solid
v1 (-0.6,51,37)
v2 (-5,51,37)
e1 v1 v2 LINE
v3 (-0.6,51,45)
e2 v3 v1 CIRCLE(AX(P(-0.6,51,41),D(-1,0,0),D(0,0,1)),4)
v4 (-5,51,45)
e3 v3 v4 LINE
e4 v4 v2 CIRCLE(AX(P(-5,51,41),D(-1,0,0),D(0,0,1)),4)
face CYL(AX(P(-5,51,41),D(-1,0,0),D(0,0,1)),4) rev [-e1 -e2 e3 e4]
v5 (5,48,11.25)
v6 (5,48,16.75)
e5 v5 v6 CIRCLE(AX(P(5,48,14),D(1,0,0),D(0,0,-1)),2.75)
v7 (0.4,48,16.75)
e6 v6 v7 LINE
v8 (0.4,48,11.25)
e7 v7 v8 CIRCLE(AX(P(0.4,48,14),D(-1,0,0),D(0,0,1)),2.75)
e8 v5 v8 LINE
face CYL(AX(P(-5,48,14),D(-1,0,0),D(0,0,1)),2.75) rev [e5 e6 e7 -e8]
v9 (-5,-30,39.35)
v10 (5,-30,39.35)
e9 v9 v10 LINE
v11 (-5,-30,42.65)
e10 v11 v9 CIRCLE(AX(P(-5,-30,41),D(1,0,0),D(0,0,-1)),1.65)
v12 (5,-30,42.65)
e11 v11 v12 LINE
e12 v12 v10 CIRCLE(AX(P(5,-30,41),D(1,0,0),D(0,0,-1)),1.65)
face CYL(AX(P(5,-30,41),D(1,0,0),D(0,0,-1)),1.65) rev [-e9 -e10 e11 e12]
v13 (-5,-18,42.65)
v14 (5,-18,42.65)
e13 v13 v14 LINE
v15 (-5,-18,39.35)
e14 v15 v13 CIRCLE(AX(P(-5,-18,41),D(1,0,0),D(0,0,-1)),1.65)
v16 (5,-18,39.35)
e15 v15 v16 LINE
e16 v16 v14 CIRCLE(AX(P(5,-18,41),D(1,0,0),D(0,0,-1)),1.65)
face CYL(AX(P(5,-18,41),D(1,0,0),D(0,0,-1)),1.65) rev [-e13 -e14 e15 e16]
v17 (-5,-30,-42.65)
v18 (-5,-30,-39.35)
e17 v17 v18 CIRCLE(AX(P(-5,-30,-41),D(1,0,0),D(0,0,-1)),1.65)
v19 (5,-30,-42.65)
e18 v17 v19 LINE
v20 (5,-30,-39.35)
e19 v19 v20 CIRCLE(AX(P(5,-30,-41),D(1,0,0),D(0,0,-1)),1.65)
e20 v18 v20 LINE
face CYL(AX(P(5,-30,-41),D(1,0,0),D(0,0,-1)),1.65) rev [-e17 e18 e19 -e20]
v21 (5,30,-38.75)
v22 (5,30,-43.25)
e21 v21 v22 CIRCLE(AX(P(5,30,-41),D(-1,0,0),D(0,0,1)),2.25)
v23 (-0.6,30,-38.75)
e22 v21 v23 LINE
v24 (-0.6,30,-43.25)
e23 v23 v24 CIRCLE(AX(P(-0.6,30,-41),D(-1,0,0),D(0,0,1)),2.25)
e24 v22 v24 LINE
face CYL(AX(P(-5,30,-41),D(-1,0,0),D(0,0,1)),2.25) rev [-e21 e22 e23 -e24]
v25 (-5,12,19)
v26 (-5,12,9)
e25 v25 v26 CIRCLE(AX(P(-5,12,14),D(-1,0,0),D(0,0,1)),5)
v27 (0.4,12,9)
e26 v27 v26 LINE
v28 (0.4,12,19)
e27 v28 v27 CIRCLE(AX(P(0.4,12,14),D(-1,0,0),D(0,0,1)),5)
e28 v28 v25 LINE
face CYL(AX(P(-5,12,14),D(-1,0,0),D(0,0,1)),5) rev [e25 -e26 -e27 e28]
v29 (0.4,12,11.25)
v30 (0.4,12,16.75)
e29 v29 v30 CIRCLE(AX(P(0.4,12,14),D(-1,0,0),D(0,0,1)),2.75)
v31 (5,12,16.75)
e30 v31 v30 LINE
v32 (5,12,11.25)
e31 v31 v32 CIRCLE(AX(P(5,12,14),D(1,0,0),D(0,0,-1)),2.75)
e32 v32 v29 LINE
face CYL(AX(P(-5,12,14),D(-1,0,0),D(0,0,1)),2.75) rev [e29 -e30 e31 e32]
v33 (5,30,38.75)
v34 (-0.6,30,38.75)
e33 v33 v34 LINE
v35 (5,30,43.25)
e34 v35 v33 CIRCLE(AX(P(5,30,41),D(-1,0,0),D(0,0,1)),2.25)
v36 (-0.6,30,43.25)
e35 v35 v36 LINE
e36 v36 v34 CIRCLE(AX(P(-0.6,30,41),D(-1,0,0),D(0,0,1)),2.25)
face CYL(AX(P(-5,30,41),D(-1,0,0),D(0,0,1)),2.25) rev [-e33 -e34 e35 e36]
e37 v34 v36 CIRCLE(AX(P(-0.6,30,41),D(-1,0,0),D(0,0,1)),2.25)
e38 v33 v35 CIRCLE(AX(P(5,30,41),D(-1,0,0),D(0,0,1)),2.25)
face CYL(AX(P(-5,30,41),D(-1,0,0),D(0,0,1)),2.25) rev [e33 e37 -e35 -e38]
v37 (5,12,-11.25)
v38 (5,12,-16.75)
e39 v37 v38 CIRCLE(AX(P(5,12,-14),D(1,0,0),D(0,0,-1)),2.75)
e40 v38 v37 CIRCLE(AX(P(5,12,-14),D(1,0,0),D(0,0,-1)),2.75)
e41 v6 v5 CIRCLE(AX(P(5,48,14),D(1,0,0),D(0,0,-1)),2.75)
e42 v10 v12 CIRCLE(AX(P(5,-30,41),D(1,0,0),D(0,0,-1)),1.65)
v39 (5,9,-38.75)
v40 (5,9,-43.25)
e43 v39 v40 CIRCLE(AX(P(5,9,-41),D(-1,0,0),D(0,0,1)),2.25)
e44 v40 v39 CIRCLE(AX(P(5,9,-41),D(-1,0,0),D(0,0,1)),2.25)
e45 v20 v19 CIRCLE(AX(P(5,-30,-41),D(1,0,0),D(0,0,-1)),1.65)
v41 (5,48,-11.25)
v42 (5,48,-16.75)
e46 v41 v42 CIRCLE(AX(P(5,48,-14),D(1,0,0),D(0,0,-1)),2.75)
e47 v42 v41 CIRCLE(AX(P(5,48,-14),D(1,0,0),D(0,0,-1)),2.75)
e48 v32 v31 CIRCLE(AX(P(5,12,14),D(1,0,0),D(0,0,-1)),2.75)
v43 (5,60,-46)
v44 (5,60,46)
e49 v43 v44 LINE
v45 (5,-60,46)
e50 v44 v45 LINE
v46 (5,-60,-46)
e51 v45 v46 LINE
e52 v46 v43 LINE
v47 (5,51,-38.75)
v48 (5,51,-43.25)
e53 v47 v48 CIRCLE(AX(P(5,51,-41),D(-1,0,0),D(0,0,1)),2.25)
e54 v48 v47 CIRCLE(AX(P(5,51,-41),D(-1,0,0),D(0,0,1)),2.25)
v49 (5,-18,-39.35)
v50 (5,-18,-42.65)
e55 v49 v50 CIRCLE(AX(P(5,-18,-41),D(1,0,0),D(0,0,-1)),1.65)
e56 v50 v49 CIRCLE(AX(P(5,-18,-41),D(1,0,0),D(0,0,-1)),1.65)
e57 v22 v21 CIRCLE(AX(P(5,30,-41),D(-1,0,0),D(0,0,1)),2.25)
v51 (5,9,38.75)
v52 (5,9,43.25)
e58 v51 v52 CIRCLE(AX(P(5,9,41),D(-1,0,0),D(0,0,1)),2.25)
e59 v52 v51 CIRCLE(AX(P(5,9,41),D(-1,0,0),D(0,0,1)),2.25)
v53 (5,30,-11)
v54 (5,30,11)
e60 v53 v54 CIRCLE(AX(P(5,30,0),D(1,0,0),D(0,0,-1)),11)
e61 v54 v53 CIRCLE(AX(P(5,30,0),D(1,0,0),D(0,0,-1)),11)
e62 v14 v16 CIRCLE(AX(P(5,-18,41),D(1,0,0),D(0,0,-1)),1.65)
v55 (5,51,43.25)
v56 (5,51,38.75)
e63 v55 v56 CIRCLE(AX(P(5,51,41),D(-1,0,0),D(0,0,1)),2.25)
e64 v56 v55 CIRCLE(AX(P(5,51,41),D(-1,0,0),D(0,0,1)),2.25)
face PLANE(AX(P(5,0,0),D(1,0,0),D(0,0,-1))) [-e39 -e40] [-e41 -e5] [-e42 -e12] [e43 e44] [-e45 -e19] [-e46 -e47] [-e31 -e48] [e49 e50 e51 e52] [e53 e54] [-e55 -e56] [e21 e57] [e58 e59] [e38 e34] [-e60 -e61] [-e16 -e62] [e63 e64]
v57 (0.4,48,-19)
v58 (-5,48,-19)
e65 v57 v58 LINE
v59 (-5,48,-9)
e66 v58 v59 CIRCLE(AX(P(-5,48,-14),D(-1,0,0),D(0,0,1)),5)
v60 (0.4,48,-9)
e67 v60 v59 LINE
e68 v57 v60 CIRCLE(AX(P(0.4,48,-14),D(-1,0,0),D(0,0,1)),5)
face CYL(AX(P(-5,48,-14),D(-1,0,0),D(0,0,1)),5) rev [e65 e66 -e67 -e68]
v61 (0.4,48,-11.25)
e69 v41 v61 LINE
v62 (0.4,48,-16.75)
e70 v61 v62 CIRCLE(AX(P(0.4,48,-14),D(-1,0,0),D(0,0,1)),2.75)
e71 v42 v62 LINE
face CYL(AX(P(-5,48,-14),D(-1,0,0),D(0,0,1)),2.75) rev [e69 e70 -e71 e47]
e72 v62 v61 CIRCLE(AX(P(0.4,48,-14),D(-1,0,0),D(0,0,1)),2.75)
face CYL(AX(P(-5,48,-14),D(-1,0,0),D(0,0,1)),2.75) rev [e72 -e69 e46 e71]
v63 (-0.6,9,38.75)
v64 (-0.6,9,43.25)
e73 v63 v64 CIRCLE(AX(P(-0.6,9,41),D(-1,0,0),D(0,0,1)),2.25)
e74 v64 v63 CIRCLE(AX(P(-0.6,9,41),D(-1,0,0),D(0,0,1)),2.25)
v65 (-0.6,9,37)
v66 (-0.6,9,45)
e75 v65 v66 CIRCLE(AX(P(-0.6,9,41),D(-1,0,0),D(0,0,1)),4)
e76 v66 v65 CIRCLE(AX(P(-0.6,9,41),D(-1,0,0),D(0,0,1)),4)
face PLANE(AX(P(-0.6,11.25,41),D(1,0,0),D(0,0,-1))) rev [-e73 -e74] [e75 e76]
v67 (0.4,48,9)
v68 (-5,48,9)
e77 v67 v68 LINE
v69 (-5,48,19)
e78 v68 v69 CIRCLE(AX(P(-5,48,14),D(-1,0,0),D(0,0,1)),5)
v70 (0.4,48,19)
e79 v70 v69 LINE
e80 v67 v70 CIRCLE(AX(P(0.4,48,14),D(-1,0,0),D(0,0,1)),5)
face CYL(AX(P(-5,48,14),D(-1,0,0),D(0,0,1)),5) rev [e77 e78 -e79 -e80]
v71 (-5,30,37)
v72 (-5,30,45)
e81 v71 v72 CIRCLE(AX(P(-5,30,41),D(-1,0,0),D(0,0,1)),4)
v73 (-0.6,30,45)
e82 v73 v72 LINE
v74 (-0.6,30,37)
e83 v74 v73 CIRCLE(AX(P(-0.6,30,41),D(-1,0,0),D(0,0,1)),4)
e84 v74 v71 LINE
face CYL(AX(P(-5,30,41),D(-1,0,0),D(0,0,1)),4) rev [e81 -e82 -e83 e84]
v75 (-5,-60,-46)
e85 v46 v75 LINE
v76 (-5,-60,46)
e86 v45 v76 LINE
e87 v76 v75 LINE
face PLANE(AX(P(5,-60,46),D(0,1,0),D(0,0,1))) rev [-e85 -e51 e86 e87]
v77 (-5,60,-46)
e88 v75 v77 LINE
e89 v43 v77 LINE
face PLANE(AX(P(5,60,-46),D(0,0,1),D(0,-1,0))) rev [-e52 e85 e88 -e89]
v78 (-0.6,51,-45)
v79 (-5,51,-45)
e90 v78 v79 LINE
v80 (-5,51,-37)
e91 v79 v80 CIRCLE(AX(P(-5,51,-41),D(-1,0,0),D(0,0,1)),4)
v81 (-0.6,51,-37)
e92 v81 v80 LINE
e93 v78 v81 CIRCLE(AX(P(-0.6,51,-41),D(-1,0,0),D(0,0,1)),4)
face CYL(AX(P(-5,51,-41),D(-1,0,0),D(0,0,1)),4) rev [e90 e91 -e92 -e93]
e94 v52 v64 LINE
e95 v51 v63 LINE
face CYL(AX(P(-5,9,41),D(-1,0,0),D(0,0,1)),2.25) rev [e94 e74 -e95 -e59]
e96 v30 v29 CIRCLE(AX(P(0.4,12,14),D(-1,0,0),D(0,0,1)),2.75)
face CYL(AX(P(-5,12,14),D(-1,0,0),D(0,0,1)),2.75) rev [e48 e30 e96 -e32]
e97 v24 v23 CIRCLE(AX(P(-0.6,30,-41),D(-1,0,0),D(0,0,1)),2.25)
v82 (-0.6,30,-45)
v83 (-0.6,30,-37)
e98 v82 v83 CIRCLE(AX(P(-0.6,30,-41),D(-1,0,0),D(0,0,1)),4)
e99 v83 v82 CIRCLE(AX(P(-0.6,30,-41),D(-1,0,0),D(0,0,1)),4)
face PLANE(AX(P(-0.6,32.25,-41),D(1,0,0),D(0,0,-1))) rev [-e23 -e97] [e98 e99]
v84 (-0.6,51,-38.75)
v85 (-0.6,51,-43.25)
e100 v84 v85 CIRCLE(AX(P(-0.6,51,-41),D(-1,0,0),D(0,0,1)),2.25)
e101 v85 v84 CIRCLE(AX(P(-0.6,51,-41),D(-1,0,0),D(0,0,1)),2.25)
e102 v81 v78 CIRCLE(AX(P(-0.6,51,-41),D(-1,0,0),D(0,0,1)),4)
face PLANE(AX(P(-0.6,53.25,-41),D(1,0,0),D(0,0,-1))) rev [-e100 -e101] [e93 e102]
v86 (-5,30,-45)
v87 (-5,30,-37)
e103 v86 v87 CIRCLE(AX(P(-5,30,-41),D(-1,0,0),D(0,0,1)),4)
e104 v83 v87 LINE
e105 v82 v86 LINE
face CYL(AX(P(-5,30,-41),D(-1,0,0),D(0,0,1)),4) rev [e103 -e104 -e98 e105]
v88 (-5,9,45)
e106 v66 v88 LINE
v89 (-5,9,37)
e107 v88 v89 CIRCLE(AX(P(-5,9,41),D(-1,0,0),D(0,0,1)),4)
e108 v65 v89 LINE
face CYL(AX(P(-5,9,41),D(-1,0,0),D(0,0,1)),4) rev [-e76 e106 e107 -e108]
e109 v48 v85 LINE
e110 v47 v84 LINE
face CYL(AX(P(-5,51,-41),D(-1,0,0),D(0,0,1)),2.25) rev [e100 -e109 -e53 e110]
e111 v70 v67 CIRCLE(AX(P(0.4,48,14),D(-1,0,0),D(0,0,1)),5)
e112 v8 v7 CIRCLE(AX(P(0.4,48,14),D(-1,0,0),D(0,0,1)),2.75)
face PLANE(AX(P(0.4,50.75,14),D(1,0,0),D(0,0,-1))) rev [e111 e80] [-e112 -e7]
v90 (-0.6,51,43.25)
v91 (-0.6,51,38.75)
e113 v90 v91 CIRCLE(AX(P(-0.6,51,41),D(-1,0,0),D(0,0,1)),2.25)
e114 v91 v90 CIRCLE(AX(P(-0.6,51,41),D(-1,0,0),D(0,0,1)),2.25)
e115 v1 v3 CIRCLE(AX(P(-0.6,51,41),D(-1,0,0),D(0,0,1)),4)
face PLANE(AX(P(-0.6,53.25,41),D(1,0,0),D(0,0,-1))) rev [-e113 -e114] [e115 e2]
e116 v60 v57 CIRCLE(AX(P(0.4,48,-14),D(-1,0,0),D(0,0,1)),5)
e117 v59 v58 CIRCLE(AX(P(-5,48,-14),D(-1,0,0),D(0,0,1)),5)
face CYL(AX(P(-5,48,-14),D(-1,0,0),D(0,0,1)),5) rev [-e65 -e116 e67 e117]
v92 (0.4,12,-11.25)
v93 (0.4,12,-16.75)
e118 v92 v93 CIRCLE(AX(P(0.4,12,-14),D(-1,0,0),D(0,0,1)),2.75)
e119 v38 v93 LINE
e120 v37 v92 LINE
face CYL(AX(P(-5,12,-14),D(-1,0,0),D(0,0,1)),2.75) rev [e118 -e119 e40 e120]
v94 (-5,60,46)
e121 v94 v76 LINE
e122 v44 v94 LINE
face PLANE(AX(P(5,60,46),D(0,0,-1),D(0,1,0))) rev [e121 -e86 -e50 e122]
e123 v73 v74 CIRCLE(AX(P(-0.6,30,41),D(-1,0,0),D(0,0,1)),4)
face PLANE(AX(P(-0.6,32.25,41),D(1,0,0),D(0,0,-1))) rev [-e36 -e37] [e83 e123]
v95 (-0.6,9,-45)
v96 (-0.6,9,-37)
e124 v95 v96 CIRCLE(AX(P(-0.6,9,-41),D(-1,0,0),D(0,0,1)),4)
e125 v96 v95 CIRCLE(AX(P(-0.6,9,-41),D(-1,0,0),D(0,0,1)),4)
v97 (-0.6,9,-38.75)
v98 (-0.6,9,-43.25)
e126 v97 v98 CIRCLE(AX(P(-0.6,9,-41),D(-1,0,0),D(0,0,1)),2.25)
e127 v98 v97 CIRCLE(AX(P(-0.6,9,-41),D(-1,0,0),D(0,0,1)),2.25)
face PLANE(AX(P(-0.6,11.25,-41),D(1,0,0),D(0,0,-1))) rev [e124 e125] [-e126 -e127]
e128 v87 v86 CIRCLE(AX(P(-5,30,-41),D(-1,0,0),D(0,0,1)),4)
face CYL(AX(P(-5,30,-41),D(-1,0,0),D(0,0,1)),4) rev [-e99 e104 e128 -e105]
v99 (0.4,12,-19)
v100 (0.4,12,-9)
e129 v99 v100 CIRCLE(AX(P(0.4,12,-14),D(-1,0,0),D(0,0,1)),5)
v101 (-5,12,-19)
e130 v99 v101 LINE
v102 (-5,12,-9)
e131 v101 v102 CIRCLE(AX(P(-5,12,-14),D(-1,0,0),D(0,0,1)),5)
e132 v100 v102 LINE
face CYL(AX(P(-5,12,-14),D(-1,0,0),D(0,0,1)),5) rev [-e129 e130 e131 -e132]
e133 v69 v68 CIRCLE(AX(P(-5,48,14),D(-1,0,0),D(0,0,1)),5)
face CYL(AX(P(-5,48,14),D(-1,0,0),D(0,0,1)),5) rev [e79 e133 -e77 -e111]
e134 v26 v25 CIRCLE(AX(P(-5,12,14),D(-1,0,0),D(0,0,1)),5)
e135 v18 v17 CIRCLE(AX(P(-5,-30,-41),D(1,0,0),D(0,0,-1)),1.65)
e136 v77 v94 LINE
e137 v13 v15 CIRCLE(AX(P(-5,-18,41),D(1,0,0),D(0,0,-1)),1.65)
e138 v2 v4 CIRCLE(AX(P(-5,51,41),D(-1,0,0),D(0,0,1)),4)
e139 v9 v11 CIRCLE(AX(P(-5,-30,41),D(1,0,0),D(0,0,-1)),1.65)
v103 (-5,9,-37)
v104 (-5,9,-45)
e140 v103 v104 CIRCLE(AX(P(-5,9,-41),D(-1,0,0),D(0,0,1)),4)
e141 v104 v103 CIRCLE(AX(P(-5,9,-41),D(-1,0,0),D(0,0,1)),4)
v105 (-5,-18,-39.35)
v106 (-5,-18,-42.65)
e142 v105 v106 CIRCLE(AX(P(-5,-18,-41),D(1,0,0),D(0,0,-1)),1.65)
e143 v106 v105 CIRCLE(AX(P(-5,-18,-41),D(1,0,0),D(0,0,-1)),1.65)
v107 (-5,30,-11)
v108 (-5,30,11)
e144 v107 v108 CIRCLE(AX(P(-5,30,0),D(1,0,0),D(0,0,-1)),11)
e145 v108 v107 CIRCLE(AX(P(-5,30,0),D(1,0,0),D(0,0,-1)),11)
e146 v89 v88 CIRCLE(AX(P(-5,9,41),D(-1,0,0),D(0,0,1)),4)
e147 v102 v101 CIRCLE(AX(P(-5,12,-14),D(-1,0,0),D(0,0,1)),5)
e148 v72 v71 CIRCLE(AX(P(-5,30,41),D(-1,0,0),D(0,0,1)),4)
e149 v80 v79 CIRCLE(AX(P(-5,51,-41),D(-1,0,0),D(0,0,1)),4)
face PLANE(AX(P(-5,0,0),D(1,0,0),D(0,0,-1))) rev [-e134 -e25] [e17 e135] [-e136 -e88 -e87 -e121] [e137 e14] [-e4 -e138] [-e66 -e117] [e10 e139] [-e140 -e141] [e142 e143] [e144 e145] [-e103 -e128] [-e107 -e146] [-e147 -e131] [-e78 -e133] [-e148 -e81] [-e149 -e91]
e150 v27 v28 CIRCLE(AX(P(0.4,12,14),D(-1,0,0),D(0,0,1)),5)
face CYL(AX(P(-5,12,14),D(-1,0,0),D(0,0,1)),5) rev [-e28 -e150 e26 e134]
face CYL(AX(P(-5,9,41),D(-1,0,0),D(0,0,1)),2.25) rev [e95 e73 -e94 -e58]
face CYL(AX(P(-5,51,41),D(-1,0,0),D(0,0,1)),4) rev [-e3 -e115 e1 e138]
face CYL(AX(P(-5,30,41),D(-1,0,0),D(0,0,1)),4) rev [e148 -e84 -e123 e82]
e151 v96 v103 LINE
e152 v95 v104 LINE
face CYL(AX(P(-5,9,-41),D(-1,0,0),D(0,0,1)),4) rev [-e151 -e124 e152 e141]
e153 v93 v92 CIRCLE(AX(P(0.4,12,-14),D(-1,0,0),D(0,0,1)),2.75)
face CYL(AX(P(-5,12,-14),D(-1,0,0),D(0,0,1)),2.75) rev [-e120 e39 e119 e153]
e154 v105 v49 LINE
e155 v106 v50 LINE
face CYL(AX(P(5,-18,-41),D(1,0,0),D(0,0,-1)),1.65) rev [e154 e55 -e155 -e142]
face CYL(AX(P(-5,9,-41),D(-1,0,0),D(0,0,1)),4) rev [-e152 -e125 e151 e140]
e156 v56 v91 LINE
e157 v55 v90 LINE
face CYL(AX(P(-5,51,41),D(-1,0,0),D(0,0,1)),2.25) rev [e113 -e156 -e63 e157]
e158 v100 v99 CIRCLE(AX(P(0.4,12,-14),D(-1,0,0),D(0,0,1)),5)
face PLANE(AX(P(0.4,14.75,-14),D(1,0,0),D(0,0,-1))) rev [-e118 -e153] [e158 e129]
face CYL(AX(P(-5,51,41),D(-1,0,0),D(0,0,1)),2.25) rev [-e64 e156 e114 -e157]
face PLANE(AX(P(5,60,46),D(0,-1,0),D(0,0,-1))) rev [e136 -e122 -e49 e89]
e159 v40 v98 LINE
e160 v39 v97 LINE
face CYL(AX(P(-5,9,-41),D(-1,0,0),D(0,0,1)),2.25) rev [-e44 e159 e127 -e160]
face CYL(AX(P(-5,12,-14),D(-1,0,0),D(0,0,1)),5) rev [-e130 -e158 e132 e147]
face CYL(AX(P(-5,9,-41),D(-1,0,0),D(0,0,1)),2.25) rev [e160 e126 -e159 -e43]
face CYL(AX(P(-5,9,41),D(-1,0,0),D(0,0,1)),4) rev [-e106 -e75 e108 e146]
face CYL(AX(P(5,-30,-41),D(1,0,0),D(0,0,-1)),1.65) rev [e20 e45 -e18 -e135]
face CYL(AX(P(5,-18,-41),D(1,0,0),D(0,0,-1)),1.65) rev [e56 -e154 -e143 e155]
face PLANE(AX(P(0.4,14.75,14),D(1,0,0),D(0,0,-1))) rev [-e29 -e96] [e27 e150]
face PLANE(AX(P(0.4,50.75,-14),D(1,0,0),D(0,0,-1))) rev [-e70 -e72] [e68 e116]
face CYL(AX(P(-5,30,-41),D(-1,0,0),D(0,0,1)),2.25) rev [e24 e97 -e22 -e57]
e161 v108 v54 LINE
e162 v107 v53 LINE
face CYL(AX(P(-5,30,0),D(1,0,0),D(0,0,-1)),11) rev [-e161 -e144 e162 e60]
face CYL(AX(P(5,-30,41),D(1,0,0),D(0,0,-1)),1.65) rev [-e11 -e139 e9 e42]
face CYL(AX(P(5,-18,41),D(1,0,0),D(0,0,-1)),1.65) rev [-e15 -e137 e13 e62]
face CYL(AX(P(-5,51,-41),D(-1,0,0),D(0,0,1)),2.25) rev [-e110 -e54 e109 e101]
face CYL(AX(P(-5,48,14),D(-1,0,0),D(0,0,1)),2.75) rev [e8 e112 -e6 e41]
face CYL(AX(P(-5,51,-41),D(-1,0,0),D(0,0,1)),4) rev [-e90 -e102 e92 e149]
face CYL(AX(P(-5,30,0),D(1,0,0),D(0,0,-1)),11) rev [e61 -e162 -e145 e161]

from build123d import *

# Parameters (mm, degrees)
SKETCH1_W                                           = 92
SKETCH1_H                                           = 120
BOSS_EXTRUDE1_DEPTH                                 = 5
SKETCH2_R                                           = 11
CUT_EXTRUDE1_DEPTH                                  = 77.26270386
M4_TAPPED_HOLE1_D                                   = 3.3
CBORE_FOR_M4_HEX_SOCKET_HEAD_CAP_SCREW1_D           = 4.5
CBORE_FOR_M4_HEX_SOCKET_HEAD_CAP_SCREW1_CBORE_D     = 8
CBORE_FOR_M4_HEX_SOCKET_HEAD_CAP_SCREW1_CBORE_DEPTH = 4.4
CBORE_FOR_M5_HEX_SOCKET_HEAD_CAP_SCREW1_D           = 5.5
CBORE_FOR_M5_HEX_SOCKET_HEAD_CAP_SCREW1_DEPTH       = 10.1
CBORE_FOR_M5_HEX_SOCKET_HEAD_CAP_SCREW1_CBORE_D     = 10
CBORE_FOR_M5_HEX_SOCKET_HEAD_CAP_SCREW1_CBORE_DEPTH = 5.4
CBORE_FOR_M5_HEX_SOCKET_HEAD_CAP_SCREW1_TIP         = 1.652366702


with BuildPart() as part:
    # Sketch1 → Boss-Extrude1 (new, symmetric)
    with BuildSketch(Plane(origin=(0, 0, 0), x_dir=(0, 0, -1), z_dir=(1, 0, 0))):
        Rectangle(SKETCH1_W, SKETCH1_H)
    extrude(amount=BOSS_EXTRUDE1_DEPTH, both=True)

    # Sketch2 → Cut-Extrude1 (cut, through all)
    with BuildSketch(Plane(origin=(5, 0, 0), x_dir=(0, 0, -1), z_dir=(1, 0, 0))):
        with Locations((0, 30)):
            Circle(SKETCH2_R)
    extrude(amount=-CUT_EXTRUDE1_DEPTH, mode=Mode.SUBTRACT)

    # M4 Tapped Hole1 (through all)
    with Locations(Plane(origin=(5, 0, 0), x_dir=(0, 0, -1), z_dir=(1, 0, 0))):
        with Locations((-41, -30), (-41, -18), (41, -30), (41, -18)):
            Hole(M4_TAPPED_HOLE1_D / 2)

    # CBORE for M4 Hex Socket Head Cap Screw1 (through all)
    with Locations(Plane.ZY.offset(5)):
        with Locations((-41, 51), (-41, 30), (-41, 9), (41, 51), (41, 30), (41, 9)):
            CounterBoreHole(CBORE_FOR_M4_HEX_SOCKET_HEAD_CAP_SCREW1_D / 2, CBORE_FOR_M4_HEX_SOCKET_HEAD_CAP_SCREW1_CBORE_D / 2, CBORE_FOR_M4_HEX_SOCKET_HEAD_CAP_SCREW1_CBORE_DEPTH)

    # CBORE for M5 Hex Socket Head Cap Screw1
    with Locations(Plane.ZY.offset(5)):
        with Locations((-14, 48), (14, 48), (-14, 12), (14, 12)):
            CounterBoreHole(CBORE_FOR_M5_HEX_SOCKET_HEAD_CAP_SCREW1_D / 2, CBORE_FOR_M5_HEX_SOCKET_HEAD_CAP_SCREW1_CBORE_D / 2, CBORE_FOR_M5_HEX_SOCKET_HEAD_CAP_SCREW1_CBORE_DEPTH, depth=CBORE_FOR_M5_HEX_SOCKET_HEAD_CAP_SCREW1_DEPTH)
            with Locations((0, 0, -(CBORE_FOR_M5_HEX_SOCKET_HEAD_CAP_SCREW1_DEPTH + CBORE_FOR_M5_HEX_SOCKET_HEAD_CAP_SCREW1_TIP / 2))):  # 118° drill point
                Cone(0, CBORE_FOR_M5_HEX_SOCKET_HEAD_CAP_SCREW1_D / 2, CBORE_FOR_M5_HEX_SOCKET_HEAD_CAP_SCREW1_TIP, mode=Mode.SUBTRACT)


solid = part.part
